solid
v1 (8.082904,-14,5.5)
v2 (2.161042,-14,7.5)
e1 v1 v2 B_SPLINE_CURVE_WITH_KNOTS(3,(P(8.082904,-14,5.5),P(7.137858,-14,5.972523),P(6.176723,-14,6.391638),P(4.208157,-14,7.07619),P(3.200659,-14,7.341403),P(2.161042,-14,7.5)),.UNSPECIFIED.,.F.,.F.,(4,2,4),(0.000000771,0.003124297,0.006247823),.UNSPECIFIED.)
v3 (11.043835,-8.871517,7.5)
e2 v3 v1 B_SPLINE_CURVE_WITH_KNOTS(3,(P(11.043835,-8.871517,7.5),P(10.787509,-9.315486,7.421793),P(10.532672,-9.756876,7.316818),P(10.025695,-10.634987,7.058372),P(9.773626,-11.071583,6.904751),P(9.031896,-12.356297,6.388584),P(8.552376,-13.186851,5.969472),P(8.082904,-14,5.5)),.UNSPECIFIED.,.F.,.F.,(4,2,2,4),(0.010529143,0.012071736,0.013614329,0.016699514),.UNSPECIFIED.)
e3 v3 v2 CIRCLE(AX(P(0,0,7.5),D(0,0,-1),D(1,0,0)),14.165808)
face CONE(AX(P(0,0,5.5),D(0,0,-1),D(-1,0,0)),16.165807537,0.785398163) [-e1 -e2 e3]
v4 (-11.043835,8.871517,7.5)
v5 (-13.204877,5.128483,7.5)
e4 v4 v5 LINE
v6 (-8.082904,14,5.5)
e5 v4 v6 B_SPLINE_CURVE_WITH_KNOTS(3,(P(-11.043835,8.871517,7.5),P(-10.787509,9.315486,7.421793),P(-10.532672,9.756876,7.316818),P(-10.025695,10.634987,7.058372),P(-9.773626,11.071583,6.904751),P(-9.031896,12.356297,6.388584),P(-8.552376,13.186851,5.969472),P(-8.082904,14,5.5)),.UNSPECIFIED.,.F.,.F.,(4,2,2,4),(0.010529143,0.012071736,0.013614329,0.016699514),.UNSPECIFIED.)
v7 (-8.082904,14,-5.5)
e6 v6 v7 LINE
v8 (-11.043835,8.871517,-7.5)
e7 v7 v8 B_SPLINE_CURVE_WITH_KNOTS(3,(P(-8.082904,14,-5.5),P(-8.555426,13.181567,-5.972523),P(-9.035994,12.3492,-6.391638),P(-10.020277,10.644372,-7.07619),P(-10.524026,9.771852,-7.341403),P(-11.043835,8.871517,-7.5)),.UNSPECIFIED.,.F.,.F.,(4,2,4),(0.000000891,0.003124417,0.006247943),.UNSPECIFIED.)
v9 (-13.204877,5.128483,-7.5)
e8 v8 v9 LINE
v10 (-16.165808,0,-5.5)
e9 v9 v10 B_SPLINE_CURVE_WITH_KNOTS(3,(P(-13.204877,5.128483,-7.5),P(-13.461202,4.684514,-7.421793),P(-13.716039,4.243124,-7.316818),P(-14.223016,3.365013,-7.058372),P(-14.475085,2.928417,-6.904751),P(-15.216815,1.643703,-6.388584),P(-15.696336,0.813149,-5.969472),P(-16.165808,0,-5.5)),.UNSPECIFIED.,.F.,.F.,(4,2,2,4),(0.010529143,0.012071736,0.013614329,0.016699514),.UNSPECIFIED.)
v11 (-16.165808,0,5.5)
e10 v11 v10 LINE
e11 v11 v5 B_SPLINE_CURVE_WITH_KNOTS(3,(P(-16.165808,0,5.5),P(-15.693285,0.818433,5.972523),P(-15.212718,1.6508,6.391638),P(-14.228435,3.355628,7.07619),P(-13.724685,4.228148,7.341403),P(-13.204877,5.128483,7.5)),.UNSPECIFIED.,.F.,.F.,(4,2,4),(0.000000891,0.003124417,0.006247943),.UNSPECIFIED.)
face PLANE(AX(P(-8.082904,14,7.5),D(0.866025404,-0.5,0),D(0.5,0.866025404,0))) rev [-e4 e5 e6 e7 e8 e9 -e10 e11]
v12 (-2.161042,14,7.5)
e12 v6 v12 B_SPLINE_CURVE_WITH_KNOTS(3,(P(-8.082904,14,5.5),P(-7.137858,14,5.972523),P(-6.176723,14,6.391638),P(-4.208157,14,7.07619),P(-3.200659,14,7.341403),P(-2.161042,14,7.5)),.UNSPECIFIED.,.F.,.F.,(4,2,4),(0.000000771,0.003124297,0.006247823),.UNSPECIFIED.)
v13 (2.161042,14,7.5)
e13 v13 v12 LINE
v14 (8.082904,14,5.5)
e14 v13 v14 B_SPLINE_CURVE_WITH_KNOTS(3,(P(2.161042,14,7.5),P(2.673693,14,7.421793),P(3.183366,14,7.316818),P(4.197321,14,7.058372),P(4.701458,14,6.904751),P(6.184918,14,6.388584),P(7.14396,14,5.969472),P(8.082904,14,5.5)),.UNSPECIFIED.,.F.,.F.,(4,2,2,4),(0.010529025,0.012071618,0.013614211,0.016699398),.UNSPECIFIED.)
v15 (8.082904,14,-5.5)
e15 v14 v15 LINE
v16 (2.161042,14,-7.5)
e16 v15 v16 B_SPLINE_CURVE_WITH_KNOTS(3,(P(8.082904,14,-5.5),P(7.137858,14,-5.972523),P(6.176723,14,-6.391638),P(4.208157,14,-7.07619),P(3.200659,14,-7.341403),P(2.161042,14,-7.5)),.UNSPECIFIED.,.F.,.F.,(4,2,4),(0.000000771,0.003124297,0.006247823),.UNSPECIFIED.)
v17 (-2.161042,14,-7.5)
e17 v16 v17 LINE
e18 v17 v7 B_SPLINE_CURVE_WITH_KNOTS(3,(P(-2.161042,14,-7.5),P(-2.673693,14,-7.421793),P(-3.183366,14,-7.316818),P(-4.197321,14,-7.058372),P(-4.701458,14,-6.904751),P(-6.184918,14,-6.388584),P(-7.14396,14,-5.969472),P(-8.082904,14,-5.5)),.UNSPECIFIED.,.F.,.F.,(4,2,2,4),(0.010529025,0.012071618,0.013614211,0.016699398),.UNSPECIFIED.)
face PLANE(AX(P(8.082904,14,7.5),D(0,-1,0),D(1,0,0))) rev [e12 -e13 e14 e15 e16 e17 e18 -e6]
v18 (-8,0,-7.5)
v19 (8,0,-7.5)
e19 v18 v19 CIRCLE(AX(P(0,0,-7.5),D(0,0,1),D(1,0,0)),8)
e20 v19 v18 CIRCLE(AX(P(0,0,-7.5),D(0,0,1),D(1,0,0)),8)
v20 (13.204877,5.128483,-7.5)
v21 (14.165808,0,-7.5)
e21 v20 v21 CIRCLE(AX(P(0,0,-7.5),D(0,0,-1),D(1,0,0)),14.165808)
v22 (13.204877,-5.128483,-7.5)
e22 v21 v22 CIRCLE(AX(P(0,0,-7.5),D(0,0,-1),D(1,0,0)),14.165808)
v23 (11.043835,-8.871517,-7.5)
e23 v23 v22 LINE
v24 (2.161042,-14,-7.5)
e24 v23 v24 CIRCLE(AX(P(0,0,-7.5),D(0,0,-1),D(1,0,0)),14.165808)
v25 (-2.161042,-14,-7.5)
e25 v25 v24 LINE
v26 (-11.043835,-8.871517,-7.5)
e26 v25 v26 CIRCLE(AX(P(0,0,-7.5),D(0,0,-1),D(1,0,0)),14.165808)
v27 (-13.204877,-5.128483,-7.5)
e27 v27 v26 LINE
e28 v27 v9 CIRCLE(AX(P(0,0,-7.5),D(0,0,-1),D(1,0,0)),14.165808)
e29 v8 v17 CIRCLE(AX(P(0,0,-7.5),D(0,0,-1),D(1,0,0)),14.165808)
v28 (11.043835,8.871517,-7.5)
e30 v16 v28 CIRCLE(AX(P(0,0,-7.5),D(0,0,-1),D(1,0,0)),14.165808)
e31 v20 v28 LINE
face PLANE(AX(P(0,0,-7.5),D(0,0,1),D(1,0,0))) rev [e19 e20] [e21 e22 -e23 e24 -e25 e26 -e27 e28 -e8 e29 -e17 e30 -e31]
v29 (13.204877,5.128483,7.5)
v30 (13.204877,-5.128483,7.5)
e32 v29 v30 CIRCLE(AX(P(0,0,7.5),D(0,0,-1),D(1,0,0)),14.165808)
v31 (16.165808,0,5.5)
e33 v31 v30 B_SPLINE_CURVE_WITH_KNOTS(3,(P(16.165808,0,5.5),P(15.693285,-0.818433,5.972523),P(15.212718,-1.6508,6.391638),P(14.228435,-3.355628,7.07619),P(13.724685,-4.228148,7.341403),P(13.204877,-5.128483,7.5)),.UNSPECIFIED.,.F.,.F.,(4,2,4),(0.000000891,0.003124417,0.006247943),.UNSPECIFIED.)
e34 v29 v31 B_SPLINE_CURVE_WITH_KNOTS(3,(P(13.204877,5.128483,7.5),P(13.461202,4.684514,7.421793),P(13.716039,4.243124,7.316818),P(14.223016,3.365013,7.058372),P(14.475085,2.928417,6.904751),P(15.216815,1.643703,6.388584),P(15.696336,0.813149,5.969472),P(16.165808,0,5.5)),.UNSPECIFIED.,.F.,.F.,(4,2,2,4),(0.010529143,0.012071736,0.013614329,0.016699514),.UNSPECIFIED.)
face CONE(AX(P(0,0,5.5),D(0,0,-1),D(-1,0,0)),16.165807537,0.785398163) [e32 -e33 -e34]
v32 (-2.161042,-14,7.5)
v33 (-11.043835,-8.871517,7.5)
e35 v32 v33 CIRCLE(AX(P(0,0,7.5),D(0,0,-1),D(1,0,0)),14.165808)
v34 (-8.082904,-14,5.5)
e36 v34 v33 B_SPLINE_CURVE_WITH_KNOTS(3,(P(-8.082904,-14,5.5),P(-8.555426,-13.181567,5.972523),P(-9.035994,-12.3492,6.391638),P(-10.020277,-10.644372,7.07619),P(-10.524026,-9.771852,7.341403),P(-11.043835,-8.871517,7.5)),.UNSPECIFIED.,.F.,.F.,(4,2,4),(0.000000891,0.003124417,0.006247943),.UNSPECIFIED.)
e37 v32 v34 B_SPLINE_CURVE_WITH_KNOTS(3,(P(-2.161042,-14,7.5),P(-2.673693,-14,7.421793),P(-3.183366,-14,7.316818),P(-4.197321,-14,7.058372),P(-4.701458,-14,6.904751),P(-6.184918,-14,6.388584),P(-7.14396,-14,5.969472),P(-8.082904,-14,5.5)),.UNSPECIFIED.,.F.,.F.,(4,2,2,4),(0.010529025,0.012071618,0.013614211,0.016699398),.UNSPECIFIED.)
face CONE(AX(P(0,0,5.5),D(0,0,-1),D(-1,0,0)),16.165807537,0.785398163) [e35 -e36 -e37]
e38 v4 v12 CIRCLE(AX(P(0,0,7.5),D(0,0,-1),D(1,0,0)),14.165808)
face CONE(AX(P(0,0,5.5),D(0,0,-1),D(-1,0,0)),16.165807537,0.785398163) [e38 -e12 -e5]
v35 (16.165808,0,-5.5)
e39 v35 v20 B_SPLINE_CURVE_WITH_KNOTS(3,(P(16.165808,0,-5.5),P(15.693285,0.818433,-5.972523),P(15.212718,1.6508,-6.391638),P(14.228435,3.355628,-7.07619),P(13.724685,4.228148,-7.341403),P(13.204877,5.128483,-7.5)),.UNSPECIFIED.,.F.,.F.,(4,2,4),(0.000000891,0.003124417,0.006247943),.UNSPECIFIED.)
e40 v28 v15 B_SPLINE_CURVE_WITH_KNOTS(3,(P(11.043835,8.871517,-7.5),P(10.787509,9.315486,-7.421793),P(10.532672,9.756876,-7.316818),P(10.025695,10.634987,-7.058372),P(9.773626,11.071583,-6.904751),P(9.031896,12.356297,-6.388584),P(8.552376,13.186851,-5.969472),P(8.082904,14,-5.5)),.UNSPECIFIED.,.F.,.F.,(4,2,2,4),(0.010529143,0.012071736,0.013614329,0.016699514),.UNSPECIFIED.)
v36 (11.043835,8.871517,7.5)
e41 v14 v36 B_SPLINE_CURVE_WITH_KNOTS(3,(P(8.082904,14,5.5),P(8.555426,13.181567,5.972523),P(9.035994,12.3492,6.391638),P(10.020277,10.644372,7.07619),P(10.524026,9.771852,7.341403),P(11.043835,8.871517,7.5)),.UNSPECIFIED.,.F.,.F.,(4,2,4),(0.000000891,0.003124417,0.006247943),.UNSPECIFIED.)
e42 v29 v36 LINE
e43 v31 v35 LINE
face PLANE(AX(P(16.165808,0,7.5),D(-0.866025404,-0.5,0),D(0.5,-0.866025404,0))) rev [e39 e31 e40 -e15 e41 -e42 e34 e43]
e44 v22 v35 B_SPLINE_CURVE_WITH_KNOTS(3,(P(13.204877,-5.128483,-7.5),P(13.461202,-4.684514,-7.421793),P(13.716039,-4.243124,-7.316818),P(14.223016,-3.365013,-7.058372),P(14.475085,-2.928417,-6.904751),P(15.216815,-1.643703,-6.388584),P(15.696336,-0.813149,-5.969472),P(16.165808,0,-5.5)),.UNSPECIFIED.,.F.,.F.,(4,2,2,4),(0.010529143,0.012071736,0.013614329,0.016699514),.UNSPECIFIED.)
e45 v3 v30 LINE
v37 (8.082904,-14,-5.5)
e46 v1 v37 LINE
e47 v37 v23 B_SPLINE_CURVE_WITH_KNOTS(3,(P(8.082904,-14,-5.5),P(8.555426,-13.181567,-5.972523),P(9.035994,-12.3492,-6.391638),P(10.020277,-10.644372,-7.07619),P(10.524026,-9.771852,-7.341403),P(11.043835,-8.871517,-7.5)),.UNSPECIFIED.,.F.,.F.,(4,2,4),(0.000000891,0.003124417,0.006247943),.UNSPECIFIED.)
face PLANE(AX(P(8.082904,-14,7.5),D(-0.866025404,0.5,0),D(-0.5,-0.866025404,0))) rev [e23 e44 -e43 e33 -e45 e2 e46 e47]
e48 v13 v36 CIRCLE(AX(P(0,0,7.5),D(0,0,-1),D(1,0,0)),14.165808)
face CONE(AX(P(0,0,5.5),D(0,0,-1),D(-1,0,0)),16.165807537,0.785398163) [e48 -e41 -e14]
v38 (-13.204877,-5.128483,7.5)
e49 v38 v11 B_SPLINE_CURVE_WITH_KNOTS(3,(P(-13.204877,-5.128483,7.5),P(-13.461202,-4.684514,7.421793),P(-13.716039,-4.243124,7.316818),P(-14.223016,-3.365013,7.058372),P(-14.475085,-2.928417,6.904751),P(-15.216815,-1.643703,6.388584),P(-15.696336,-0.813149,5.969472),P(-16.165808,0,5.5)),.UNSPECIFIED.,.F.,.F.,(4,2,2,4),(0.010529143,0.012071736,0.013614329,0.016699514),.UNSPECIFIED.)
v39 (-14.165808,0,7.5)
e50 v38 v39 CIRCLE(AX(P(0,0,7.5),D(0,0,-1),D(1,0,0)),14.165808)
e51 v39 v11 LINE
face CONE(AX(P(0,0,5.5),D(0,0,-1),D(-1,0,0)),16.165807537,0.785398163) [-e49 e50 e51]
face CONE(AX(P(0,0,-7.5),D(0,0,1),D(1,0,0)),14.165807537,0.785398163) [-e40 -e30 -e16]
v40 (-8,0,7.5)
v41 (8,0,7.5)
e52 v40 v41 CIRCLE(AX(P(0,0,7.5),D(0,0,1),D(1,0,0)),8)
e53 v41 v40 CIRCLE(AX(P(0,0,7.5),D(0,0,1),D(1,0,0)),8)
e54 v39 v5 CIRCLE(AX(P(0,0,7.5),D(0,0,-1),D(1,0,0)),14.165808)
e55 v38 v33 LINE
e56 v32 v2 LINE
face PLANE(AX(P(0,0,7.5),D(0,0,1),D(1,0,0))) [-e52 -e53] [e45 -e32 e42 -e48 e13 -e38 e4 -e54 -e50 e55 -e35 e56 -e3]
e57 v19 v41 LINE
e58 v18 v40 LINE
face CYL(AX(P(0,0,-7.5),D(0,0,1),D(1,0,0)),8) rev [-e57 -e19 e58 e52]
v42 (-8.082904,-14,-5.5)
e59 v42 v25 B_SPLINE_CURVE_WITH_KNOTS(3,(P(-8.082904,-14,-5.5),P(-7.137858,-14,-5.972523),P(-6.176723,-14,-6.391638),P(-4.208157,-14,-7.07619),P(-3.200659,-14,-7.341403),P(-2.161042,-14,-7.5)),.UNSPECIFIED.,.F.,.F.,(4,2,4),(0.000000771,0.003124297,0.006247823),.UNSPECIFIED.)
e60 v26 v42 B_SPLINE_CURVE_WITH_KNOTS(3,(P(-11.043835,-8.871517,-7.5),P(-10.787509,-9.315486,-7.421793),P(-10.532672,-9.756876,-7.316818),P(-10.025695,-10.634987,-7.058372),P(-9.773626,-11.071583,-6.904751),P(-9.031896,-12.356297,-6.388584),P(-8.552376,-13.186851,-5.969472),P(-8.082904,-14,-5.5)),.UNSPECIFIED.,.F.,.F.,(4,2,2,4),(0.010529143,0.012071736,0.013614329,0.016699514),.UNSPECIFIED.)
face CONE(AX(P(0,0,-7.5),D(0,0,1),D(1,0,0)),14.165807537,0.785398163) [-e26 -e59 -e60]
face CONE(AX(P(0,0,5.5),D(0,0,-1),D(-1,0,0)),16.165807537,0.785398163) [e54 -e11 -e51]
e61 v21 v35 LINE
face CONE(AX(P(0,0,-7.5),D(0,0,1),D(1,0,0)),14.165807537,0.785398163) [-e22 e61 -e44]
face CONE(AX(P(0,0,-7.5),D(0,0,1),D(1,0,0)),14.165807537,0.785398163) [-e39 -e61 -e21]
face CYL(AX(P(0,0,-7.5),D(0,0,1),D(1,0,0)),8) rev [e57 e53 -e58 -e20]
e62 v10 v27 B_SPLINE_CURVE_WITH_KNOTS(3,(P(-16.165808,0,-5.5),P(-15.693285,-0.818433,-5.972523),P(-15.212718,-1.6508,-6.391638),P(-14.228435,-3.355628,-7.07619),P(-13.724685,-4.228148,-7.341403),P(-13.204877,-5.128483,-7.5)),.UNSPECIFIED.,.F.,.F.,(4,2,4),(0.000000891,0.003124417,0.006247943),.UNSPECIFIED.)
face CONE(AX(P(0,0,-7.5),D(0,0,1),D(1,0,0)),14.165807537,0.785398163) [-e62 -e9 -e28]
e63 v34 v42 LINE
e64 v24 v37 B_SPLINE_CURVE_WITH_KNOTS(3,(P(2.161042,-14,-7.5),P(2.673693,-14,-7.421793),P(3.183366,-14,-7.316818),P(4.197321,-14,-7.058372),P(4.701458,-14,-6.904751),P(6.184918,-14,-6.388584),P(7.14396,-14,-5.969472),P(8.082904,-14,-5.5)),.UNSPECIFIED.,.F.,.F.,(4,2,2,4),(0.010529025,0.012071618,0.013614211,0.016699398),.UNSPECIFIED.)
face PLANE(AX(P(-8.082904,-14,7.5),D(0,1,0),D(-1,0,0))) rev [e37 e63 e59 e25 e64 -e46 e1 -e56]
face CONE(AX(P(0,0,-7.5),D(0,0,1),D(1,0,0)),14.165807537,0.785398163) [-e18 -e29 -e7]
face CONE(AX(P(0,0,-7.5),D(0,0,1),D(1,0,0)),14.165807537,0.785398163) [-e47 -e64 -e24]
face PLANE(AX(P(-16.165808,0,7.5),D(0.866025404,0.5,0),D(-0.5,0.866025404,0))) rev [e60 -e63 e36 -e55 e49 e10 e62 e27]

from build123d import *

# Parameters (mm, degrees)
HEX_BODY_15_THICK_DEPTH = 7.5
BORE_PROFILE_16_R       = 8
BORE_16_THRU_DEPTH      = 7.5


with BuildPart() as part:
    # Hex Profile 28 AF → Hex Body 15 Thick (new, symmetric)
    with BuildSketch(Plane.XY):
        Polygon((16.165807537, 0), (8.082903769, 14), (-8.082903769, 14), (-16.165807537, 0), (-8.082903769, -14), (8.082903769, -14), align=None)
    extrude(amount=HEX_BODY_15_THICK_DEPTH, both=True)

    # Bore Profile Ø16 → Bore Ø16 Thru (cut, symmetric)
    with BuildSketch(Plane.XY):
        Circle(BORE_PROFILE_16_R)
    extrude(amount=BORE_16_THRU_DEPTH, both=True, mode=Mode.SUBTRACT)

    # Chamfer Profile 2mm → Double-Sided Chamfer 2mm (revolve, cut)
    with BuildSketch(Plane(origin=(0, 0, 0), x_dir=(1, 0, 0), z_dir=(0, 1, 0))):
        Polygon((16.165807537, 7.5), (16.165807537, 5.5), (14.165807537, 7.5), align=None)
        Polygon((16.165807537, -7.5), (16.165807537, -5.5), (14.165807537, -7.5), align=None)
    revolve(axis=Axis((0, 0, 1000), (0, 0, -1)), mode=Mode.SUBTRACT)


solid = part.part
